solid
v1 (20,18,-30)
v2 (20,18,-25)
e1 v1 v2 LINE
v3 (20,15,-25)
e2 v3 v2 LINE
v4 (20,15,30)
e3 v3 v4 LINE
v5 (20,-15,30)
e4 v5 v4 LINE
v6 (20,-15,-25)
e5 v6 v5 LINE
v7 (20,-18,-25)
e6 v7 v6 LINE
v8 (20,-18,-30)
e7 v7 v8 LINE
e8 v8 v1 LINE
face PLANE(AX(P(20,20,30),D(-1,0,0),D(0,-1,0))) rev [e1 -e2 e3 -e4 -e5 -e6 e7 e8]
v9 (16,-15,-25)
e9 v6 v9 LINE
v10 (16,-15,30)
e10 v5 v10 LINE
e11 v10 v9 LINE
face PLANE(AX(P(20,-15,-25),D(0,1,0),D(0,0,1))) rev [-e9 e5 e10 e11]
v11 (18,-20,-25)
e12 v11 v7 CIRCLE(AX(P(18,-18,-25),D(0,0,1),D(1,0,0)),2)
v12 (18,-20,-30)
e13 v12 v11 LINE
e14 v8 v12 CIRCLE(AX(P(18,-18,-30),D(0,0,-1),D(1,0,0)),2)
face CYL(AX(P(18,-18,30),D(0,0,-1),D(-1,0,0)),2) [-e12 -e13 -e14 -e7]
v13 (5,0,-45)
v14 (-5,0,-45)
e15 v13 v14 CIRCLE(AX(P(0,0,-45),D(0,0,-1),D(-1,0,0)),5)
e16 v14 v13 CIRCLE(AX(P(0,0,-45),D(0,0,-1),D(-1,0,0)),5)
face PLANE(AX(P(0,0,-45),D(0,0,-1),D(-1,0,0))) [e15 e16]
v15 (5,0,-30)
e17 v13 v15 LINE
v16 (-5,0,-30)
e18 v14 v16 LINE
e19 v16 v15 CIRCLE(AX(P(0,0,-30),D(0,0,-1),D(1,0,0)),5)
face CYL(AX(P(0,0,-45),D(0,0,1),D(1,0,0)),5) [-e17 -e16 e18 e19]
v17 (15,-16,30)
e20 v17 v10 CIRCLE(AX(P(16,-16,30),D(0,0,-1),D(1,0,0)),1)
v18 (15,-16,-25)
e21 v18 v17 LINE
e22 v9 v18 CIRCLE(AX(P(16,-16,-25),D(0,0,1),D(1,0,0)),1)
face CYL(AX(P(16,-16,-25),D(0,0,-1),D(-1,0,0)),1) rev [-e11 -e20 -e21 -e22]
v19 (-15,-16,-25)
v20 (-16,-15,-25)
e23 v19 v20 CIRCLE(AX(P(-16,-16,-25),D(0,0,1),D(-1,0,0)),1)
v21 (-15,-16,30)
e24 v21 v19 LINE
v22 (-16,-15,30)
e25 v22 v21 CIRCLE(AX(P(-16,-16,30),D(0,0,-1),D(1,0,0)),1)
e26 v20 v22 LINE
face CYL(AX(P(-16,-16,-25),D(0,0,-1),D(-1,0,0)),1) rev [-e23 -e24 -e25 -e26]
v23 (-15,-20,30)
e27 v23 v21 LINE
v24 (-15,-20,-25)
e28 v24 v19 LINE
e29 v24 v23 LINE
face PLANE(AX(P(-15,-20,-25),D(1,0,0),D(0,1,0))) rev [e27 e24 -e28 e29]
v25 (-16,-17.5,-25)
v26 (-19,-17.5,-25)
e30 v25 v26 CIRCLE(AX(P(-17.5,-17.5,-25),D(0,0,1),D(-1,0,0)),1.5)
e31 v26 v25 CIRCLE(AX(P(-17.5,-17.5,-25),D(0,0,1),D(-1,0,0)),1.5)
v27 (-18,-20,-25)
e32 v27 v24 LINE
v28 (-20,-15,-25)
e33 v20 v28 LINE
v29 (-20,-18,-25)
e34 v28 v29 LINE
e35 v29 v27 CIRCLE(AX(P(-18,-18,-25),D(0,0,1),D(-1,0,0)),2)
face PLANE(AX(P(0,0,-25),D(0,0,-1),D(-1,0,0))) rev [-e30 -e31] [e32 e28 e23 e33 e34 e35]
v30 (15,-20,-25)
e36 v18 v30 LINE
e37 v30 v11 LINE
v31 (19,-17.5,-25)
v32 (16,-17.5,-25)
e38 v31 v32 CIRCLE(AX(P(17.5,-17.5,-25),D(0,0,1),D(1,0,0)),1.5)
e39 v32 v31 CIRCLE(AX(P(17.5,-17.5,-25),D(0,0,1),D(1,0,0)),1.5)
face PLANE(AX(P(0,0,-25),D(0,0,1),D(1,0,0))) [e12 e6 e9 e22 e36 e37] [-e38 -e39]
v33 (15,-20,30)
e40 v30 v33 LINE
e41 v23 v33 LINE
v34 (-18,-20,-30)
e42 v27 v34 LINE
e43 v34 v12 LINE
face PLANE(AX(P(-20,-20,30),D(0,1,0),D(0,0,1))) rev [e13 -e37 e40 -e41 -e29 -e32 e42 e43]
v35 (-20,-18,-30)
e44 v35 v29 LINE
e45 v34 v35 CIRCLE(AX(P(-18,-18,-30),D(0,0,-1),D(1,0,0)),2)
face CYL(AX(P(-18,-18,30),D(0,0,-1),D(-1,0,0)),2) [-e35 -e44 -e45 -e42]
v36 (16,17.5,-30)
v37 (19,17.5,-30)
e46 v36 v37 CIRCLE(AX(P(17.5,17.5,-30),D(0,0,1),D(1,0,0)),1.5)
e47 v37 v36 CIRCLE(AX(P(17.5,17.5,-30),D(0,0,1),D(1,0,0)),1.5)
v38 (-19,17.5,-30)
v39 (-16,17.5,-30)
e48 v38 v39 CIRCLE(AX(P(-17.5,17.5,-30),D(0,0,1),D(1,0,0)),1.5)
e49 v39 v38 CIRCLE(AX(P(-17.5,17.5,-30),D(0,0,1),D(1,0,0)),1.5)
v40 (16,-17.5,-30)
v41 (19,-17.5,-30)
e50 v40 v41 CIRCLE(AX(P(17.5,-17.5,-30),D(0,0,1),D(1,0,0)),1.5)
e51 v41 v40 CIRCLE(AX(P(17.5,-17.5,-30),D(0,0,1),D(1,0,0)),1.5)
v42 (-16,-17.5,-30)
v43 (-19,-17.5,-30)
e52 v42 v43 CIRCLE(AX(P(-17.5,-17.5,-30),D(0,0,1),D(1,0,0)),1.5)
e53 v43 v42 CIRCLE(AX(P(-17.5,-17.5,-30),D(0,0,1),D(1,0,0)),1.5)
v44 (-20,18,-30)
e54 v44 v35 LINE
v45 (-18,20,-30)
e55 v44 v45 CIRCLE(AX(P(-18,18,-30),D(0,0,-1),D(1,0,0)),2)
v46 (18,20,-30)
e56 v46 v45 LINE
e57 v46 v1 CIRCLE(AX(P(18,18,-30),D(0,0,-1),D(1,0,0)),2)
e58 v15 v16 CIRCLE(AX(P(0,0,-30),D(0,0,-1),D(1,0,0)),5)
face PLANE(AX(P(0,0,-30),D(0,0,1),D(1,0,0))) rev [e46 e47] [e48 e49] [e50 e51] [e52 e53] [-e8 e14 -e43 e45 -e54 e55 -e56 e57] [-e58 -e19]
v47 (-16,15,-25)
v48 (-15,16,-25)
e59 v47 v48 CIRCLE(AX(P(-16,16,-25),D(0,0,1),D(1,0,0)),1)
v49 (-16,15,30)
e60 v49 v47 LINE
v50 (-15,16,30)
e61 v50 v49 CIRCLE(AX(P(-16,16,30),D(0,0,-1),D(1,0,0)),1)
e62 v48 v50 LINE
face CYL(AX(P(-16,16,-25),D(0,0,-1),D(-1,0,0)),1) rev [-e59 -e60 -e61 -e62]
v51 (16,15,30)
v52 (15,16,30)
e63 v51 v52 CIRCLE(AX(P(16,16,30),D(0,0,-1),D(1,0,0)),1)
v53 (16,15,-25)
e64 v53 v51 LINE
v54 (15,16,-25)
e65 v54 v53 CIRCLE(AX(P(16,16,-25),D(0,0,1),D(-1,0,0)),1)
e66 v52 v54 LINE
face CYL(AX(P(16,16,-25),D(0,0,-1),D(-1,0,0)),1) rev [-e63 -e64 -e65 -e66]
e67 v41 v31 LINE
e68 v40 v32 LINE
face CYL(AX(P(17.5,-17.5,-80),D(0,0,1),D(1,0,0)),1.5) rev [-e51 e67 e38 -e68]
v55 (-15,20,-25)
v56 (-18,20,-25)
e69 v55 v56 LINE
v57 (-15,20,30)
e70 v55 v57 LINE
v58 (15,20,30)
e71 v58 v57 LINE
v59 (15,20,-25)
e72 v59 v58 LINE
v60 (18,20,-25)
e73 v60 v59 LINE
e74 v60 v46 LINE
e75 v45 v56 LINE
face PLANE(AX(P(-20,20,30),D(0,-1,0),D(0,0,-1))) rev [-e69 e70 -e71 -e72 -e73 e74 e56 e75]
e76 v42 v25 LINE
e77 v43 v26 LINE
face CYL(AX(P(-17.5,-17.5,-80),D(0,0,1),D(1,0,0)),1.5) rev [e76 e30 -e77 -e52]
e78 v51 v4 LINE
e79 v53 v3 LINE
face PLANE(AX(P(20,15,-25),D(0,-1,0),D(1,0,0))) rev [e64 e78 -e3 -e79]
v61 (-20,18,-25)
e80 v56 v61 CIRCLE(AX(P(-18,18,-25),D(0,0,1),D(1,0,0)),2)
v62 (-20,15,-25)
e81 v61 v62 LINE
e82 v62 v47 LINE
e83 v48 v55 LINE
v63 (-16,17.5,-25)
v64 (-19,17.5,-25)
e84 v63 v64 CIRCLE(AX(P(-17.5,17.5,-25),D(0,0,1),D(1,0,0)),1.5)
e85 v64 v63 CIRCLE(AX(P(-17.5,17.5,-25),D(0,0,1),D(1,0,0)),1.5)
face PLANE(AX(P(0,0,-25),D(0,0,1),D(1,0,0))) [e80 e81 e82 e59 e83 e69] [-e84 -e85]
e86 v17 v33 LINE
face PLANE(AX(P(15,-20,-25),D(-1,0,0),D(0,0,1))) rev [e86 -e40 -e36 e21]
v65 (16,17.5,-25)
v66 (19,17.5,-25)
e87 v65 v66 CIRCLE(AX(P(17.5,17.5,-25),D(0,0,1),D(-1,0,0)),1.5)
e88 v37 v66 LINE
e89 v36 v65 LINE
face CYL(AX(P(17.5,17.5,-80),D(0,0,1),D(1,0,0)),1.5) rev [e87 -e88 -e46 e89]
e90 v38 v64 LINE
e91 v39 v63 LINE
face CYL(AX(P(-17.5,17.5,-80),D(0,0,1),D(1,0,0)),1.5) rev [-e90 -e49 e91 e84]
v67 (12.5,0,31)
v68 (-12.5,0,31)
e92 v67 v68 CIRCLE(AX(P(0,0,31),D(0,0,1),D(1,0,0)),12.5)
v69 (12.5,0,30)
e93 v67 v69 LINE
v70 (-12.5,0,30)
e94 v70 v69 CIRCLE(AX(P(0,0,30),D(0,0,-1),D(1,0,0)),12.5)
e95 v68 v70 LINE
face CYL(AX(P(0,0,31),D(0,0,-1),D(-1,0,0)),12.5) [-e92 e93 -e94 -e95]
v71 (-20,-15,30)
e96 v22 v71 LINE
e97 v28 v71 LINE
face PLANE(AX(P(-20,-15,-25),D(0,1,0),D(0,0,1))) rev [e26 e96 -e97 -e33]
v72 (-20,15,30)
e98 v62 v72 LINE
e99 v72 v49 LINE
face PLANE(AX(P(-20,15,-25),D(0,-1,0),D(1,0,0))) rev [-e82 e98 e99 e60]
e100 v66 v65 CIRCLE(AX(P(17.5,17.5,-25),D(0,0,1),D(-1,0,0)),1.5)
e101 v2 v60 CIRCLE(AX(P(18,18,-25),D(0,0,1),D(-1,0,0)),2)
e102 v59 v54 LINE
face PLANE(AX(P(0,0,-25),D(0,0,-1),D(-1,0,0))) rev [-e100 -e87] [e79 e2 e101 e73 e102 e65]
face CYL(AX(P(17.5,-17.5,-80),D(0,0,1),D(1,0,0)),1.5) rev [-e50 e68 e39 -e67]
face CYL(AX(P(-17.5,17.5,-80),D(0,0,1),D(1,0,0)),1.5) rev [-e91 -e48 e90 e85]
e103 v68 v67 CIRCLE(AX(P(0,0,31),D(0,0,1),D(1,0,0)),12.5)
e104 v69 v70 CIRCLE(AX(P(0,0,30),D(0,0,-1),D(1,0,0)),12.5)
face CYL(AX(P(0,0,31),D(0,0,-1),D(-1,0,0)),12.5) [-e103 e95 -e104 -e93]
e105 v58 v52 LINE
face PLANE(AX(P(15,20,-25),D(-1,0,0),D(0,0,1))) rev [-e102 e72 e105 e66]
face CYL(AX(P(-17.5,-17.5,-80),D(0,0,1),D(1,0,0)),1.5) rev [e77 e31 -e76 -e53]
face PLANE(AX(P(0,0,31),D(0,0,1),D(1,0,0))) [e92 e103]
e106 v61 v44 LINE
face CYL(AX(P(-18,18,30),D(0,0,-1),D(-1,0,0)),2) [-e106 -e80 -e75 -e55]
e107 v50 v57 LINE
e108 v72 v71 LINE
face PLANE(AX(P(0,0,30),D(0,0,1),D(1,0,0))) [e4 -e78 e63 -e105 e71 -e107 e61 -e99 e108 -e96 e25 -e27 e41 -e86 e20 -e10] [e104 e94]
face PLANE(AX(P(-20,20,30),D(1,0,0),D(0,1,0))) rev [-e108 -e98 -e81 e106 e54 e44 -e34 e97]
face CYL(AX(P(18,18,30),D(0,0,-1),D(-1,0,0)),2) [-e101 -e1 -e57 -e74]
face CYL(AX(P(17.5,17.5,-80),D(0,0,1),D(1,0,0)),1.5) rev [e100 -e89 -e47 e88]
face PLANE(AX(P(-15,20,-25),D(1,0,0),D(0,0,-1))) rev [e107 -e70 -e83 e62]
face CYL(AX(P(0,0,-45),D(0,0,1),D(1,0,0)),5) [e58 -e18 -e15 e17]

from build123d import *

# Parameters (mm, degrees)
SKETCH1_W           = 40
SKETCH1_H           = 40
BOSS_EXTRUDE1_DEPTH = 30
SKETCH2_W           = 5
SKETCH2_H           = 5
CUT_EXTRUDE1_DEPTH  = 55
SKETCH3_R           = 1.5
CUT_EXTRUDE2_DEPTH  = 55
FILLET1_R           = 2
SKETCH4_R           = 12.5
BOSS_EXTRUDE2_DEPTH = 1
FILLET2_R           = 1
SKETCH5_R           = 5
BOSS_EXTRUDE3_DEPTH = 15


with BuildPart() as part:
    # Sketch1 → Boss-Extrude1 (new, symmetric)
    with BuildSketch(Plane.XY):
        Rectangle(SKETCH1_W, SKETCH1_H)
    extrude(amount=BOSS_EXTRUDE1_DEPTH, both=True)

    # Sketch2 → Cut-Extrude1 (cut)
    with BuildSketch(Plane.XY.offset(30)):
        with Locations((-17.5, 17.5)):
            Rectangle(SKETCH2_W, SKETCH2_H)
        with Locations((17.5, 17.5)):
            Rectangle(SKETCH2_W, SKETCH2_H)
        with Locations((17.5, -17.5)):
            Rectangle(SKETCH2_W, SKETCH2_H)
        with Locations((-17.5, -17.5)):
            Rectangle(SKETCH2_W, SKETCH2_H)
    extrude(amount=-CUT_EXTRUDE1_DEPTH, mode=Mode.SUBTRACT)

    # Sketch3 → Cut-Extrude2 (cut)
    with BuildSketch(Plane.XY.offset(-25)):
        with Locations((-17.5, 17.5)):
            Circle(SKETCH3_R)
        with Locations((17.5, 17.5)):
            Circle(SKETCH3_R)
        with Locations((17.5, -17.5)):
            Circle(SKETCH3_R)
        with Locations((-17.5, -17.5)):
            Circle(SKETCH3_R)
    extrude(amount=-CUT_EXTRUDE2_DEPTH, mode=Mode.SUBTRACT)

    # Fillet1
    fillet1_edges = [part.edges().sort_by_distance(p)[0] for p in [
        (20, -20, -27.5),
        (-20, -20, -27.5),
        (-20, 20, -27.5),
        (20, 20, -27.5),
    ]]
    fillet(fillet1_edges, radius=FILLET1_R)

    # Sketch4 → Boss-Extrude2 (add, symmetric)
    with BuildSketch(Plane.XY.offset(30)):
        Circle(SKETCH4_R)
    extrude(amount=BOSS_EXTRUDE2_DEPTH, both=True)

    # Fillet2
    fillet2_edges = [part.edges().sort_by_distance(p)[0] for p in [
        (-15, -15, 2.5),
        (15, -15, 2.5),
        (15, 15, 2.5),
        (-15, 15, 2.5),
    ]]
    fillet(fillet2_edges, radius=FILLET2_R)

    # Sketch5 → Boss-Extrude3 (add)
    with BuildSketch(Plane(origin=(0, 0, -30), x_dir=(-1, 0, 0), z_dir=(0, 0, -1))):
        with Locations(Location((0, 0, 0), (0, 0, 180))):
            Circle(SKETCH5_R)
    extrude(amount=BOSS_EXTRUDE3_DEPTH)


solid = part.part
